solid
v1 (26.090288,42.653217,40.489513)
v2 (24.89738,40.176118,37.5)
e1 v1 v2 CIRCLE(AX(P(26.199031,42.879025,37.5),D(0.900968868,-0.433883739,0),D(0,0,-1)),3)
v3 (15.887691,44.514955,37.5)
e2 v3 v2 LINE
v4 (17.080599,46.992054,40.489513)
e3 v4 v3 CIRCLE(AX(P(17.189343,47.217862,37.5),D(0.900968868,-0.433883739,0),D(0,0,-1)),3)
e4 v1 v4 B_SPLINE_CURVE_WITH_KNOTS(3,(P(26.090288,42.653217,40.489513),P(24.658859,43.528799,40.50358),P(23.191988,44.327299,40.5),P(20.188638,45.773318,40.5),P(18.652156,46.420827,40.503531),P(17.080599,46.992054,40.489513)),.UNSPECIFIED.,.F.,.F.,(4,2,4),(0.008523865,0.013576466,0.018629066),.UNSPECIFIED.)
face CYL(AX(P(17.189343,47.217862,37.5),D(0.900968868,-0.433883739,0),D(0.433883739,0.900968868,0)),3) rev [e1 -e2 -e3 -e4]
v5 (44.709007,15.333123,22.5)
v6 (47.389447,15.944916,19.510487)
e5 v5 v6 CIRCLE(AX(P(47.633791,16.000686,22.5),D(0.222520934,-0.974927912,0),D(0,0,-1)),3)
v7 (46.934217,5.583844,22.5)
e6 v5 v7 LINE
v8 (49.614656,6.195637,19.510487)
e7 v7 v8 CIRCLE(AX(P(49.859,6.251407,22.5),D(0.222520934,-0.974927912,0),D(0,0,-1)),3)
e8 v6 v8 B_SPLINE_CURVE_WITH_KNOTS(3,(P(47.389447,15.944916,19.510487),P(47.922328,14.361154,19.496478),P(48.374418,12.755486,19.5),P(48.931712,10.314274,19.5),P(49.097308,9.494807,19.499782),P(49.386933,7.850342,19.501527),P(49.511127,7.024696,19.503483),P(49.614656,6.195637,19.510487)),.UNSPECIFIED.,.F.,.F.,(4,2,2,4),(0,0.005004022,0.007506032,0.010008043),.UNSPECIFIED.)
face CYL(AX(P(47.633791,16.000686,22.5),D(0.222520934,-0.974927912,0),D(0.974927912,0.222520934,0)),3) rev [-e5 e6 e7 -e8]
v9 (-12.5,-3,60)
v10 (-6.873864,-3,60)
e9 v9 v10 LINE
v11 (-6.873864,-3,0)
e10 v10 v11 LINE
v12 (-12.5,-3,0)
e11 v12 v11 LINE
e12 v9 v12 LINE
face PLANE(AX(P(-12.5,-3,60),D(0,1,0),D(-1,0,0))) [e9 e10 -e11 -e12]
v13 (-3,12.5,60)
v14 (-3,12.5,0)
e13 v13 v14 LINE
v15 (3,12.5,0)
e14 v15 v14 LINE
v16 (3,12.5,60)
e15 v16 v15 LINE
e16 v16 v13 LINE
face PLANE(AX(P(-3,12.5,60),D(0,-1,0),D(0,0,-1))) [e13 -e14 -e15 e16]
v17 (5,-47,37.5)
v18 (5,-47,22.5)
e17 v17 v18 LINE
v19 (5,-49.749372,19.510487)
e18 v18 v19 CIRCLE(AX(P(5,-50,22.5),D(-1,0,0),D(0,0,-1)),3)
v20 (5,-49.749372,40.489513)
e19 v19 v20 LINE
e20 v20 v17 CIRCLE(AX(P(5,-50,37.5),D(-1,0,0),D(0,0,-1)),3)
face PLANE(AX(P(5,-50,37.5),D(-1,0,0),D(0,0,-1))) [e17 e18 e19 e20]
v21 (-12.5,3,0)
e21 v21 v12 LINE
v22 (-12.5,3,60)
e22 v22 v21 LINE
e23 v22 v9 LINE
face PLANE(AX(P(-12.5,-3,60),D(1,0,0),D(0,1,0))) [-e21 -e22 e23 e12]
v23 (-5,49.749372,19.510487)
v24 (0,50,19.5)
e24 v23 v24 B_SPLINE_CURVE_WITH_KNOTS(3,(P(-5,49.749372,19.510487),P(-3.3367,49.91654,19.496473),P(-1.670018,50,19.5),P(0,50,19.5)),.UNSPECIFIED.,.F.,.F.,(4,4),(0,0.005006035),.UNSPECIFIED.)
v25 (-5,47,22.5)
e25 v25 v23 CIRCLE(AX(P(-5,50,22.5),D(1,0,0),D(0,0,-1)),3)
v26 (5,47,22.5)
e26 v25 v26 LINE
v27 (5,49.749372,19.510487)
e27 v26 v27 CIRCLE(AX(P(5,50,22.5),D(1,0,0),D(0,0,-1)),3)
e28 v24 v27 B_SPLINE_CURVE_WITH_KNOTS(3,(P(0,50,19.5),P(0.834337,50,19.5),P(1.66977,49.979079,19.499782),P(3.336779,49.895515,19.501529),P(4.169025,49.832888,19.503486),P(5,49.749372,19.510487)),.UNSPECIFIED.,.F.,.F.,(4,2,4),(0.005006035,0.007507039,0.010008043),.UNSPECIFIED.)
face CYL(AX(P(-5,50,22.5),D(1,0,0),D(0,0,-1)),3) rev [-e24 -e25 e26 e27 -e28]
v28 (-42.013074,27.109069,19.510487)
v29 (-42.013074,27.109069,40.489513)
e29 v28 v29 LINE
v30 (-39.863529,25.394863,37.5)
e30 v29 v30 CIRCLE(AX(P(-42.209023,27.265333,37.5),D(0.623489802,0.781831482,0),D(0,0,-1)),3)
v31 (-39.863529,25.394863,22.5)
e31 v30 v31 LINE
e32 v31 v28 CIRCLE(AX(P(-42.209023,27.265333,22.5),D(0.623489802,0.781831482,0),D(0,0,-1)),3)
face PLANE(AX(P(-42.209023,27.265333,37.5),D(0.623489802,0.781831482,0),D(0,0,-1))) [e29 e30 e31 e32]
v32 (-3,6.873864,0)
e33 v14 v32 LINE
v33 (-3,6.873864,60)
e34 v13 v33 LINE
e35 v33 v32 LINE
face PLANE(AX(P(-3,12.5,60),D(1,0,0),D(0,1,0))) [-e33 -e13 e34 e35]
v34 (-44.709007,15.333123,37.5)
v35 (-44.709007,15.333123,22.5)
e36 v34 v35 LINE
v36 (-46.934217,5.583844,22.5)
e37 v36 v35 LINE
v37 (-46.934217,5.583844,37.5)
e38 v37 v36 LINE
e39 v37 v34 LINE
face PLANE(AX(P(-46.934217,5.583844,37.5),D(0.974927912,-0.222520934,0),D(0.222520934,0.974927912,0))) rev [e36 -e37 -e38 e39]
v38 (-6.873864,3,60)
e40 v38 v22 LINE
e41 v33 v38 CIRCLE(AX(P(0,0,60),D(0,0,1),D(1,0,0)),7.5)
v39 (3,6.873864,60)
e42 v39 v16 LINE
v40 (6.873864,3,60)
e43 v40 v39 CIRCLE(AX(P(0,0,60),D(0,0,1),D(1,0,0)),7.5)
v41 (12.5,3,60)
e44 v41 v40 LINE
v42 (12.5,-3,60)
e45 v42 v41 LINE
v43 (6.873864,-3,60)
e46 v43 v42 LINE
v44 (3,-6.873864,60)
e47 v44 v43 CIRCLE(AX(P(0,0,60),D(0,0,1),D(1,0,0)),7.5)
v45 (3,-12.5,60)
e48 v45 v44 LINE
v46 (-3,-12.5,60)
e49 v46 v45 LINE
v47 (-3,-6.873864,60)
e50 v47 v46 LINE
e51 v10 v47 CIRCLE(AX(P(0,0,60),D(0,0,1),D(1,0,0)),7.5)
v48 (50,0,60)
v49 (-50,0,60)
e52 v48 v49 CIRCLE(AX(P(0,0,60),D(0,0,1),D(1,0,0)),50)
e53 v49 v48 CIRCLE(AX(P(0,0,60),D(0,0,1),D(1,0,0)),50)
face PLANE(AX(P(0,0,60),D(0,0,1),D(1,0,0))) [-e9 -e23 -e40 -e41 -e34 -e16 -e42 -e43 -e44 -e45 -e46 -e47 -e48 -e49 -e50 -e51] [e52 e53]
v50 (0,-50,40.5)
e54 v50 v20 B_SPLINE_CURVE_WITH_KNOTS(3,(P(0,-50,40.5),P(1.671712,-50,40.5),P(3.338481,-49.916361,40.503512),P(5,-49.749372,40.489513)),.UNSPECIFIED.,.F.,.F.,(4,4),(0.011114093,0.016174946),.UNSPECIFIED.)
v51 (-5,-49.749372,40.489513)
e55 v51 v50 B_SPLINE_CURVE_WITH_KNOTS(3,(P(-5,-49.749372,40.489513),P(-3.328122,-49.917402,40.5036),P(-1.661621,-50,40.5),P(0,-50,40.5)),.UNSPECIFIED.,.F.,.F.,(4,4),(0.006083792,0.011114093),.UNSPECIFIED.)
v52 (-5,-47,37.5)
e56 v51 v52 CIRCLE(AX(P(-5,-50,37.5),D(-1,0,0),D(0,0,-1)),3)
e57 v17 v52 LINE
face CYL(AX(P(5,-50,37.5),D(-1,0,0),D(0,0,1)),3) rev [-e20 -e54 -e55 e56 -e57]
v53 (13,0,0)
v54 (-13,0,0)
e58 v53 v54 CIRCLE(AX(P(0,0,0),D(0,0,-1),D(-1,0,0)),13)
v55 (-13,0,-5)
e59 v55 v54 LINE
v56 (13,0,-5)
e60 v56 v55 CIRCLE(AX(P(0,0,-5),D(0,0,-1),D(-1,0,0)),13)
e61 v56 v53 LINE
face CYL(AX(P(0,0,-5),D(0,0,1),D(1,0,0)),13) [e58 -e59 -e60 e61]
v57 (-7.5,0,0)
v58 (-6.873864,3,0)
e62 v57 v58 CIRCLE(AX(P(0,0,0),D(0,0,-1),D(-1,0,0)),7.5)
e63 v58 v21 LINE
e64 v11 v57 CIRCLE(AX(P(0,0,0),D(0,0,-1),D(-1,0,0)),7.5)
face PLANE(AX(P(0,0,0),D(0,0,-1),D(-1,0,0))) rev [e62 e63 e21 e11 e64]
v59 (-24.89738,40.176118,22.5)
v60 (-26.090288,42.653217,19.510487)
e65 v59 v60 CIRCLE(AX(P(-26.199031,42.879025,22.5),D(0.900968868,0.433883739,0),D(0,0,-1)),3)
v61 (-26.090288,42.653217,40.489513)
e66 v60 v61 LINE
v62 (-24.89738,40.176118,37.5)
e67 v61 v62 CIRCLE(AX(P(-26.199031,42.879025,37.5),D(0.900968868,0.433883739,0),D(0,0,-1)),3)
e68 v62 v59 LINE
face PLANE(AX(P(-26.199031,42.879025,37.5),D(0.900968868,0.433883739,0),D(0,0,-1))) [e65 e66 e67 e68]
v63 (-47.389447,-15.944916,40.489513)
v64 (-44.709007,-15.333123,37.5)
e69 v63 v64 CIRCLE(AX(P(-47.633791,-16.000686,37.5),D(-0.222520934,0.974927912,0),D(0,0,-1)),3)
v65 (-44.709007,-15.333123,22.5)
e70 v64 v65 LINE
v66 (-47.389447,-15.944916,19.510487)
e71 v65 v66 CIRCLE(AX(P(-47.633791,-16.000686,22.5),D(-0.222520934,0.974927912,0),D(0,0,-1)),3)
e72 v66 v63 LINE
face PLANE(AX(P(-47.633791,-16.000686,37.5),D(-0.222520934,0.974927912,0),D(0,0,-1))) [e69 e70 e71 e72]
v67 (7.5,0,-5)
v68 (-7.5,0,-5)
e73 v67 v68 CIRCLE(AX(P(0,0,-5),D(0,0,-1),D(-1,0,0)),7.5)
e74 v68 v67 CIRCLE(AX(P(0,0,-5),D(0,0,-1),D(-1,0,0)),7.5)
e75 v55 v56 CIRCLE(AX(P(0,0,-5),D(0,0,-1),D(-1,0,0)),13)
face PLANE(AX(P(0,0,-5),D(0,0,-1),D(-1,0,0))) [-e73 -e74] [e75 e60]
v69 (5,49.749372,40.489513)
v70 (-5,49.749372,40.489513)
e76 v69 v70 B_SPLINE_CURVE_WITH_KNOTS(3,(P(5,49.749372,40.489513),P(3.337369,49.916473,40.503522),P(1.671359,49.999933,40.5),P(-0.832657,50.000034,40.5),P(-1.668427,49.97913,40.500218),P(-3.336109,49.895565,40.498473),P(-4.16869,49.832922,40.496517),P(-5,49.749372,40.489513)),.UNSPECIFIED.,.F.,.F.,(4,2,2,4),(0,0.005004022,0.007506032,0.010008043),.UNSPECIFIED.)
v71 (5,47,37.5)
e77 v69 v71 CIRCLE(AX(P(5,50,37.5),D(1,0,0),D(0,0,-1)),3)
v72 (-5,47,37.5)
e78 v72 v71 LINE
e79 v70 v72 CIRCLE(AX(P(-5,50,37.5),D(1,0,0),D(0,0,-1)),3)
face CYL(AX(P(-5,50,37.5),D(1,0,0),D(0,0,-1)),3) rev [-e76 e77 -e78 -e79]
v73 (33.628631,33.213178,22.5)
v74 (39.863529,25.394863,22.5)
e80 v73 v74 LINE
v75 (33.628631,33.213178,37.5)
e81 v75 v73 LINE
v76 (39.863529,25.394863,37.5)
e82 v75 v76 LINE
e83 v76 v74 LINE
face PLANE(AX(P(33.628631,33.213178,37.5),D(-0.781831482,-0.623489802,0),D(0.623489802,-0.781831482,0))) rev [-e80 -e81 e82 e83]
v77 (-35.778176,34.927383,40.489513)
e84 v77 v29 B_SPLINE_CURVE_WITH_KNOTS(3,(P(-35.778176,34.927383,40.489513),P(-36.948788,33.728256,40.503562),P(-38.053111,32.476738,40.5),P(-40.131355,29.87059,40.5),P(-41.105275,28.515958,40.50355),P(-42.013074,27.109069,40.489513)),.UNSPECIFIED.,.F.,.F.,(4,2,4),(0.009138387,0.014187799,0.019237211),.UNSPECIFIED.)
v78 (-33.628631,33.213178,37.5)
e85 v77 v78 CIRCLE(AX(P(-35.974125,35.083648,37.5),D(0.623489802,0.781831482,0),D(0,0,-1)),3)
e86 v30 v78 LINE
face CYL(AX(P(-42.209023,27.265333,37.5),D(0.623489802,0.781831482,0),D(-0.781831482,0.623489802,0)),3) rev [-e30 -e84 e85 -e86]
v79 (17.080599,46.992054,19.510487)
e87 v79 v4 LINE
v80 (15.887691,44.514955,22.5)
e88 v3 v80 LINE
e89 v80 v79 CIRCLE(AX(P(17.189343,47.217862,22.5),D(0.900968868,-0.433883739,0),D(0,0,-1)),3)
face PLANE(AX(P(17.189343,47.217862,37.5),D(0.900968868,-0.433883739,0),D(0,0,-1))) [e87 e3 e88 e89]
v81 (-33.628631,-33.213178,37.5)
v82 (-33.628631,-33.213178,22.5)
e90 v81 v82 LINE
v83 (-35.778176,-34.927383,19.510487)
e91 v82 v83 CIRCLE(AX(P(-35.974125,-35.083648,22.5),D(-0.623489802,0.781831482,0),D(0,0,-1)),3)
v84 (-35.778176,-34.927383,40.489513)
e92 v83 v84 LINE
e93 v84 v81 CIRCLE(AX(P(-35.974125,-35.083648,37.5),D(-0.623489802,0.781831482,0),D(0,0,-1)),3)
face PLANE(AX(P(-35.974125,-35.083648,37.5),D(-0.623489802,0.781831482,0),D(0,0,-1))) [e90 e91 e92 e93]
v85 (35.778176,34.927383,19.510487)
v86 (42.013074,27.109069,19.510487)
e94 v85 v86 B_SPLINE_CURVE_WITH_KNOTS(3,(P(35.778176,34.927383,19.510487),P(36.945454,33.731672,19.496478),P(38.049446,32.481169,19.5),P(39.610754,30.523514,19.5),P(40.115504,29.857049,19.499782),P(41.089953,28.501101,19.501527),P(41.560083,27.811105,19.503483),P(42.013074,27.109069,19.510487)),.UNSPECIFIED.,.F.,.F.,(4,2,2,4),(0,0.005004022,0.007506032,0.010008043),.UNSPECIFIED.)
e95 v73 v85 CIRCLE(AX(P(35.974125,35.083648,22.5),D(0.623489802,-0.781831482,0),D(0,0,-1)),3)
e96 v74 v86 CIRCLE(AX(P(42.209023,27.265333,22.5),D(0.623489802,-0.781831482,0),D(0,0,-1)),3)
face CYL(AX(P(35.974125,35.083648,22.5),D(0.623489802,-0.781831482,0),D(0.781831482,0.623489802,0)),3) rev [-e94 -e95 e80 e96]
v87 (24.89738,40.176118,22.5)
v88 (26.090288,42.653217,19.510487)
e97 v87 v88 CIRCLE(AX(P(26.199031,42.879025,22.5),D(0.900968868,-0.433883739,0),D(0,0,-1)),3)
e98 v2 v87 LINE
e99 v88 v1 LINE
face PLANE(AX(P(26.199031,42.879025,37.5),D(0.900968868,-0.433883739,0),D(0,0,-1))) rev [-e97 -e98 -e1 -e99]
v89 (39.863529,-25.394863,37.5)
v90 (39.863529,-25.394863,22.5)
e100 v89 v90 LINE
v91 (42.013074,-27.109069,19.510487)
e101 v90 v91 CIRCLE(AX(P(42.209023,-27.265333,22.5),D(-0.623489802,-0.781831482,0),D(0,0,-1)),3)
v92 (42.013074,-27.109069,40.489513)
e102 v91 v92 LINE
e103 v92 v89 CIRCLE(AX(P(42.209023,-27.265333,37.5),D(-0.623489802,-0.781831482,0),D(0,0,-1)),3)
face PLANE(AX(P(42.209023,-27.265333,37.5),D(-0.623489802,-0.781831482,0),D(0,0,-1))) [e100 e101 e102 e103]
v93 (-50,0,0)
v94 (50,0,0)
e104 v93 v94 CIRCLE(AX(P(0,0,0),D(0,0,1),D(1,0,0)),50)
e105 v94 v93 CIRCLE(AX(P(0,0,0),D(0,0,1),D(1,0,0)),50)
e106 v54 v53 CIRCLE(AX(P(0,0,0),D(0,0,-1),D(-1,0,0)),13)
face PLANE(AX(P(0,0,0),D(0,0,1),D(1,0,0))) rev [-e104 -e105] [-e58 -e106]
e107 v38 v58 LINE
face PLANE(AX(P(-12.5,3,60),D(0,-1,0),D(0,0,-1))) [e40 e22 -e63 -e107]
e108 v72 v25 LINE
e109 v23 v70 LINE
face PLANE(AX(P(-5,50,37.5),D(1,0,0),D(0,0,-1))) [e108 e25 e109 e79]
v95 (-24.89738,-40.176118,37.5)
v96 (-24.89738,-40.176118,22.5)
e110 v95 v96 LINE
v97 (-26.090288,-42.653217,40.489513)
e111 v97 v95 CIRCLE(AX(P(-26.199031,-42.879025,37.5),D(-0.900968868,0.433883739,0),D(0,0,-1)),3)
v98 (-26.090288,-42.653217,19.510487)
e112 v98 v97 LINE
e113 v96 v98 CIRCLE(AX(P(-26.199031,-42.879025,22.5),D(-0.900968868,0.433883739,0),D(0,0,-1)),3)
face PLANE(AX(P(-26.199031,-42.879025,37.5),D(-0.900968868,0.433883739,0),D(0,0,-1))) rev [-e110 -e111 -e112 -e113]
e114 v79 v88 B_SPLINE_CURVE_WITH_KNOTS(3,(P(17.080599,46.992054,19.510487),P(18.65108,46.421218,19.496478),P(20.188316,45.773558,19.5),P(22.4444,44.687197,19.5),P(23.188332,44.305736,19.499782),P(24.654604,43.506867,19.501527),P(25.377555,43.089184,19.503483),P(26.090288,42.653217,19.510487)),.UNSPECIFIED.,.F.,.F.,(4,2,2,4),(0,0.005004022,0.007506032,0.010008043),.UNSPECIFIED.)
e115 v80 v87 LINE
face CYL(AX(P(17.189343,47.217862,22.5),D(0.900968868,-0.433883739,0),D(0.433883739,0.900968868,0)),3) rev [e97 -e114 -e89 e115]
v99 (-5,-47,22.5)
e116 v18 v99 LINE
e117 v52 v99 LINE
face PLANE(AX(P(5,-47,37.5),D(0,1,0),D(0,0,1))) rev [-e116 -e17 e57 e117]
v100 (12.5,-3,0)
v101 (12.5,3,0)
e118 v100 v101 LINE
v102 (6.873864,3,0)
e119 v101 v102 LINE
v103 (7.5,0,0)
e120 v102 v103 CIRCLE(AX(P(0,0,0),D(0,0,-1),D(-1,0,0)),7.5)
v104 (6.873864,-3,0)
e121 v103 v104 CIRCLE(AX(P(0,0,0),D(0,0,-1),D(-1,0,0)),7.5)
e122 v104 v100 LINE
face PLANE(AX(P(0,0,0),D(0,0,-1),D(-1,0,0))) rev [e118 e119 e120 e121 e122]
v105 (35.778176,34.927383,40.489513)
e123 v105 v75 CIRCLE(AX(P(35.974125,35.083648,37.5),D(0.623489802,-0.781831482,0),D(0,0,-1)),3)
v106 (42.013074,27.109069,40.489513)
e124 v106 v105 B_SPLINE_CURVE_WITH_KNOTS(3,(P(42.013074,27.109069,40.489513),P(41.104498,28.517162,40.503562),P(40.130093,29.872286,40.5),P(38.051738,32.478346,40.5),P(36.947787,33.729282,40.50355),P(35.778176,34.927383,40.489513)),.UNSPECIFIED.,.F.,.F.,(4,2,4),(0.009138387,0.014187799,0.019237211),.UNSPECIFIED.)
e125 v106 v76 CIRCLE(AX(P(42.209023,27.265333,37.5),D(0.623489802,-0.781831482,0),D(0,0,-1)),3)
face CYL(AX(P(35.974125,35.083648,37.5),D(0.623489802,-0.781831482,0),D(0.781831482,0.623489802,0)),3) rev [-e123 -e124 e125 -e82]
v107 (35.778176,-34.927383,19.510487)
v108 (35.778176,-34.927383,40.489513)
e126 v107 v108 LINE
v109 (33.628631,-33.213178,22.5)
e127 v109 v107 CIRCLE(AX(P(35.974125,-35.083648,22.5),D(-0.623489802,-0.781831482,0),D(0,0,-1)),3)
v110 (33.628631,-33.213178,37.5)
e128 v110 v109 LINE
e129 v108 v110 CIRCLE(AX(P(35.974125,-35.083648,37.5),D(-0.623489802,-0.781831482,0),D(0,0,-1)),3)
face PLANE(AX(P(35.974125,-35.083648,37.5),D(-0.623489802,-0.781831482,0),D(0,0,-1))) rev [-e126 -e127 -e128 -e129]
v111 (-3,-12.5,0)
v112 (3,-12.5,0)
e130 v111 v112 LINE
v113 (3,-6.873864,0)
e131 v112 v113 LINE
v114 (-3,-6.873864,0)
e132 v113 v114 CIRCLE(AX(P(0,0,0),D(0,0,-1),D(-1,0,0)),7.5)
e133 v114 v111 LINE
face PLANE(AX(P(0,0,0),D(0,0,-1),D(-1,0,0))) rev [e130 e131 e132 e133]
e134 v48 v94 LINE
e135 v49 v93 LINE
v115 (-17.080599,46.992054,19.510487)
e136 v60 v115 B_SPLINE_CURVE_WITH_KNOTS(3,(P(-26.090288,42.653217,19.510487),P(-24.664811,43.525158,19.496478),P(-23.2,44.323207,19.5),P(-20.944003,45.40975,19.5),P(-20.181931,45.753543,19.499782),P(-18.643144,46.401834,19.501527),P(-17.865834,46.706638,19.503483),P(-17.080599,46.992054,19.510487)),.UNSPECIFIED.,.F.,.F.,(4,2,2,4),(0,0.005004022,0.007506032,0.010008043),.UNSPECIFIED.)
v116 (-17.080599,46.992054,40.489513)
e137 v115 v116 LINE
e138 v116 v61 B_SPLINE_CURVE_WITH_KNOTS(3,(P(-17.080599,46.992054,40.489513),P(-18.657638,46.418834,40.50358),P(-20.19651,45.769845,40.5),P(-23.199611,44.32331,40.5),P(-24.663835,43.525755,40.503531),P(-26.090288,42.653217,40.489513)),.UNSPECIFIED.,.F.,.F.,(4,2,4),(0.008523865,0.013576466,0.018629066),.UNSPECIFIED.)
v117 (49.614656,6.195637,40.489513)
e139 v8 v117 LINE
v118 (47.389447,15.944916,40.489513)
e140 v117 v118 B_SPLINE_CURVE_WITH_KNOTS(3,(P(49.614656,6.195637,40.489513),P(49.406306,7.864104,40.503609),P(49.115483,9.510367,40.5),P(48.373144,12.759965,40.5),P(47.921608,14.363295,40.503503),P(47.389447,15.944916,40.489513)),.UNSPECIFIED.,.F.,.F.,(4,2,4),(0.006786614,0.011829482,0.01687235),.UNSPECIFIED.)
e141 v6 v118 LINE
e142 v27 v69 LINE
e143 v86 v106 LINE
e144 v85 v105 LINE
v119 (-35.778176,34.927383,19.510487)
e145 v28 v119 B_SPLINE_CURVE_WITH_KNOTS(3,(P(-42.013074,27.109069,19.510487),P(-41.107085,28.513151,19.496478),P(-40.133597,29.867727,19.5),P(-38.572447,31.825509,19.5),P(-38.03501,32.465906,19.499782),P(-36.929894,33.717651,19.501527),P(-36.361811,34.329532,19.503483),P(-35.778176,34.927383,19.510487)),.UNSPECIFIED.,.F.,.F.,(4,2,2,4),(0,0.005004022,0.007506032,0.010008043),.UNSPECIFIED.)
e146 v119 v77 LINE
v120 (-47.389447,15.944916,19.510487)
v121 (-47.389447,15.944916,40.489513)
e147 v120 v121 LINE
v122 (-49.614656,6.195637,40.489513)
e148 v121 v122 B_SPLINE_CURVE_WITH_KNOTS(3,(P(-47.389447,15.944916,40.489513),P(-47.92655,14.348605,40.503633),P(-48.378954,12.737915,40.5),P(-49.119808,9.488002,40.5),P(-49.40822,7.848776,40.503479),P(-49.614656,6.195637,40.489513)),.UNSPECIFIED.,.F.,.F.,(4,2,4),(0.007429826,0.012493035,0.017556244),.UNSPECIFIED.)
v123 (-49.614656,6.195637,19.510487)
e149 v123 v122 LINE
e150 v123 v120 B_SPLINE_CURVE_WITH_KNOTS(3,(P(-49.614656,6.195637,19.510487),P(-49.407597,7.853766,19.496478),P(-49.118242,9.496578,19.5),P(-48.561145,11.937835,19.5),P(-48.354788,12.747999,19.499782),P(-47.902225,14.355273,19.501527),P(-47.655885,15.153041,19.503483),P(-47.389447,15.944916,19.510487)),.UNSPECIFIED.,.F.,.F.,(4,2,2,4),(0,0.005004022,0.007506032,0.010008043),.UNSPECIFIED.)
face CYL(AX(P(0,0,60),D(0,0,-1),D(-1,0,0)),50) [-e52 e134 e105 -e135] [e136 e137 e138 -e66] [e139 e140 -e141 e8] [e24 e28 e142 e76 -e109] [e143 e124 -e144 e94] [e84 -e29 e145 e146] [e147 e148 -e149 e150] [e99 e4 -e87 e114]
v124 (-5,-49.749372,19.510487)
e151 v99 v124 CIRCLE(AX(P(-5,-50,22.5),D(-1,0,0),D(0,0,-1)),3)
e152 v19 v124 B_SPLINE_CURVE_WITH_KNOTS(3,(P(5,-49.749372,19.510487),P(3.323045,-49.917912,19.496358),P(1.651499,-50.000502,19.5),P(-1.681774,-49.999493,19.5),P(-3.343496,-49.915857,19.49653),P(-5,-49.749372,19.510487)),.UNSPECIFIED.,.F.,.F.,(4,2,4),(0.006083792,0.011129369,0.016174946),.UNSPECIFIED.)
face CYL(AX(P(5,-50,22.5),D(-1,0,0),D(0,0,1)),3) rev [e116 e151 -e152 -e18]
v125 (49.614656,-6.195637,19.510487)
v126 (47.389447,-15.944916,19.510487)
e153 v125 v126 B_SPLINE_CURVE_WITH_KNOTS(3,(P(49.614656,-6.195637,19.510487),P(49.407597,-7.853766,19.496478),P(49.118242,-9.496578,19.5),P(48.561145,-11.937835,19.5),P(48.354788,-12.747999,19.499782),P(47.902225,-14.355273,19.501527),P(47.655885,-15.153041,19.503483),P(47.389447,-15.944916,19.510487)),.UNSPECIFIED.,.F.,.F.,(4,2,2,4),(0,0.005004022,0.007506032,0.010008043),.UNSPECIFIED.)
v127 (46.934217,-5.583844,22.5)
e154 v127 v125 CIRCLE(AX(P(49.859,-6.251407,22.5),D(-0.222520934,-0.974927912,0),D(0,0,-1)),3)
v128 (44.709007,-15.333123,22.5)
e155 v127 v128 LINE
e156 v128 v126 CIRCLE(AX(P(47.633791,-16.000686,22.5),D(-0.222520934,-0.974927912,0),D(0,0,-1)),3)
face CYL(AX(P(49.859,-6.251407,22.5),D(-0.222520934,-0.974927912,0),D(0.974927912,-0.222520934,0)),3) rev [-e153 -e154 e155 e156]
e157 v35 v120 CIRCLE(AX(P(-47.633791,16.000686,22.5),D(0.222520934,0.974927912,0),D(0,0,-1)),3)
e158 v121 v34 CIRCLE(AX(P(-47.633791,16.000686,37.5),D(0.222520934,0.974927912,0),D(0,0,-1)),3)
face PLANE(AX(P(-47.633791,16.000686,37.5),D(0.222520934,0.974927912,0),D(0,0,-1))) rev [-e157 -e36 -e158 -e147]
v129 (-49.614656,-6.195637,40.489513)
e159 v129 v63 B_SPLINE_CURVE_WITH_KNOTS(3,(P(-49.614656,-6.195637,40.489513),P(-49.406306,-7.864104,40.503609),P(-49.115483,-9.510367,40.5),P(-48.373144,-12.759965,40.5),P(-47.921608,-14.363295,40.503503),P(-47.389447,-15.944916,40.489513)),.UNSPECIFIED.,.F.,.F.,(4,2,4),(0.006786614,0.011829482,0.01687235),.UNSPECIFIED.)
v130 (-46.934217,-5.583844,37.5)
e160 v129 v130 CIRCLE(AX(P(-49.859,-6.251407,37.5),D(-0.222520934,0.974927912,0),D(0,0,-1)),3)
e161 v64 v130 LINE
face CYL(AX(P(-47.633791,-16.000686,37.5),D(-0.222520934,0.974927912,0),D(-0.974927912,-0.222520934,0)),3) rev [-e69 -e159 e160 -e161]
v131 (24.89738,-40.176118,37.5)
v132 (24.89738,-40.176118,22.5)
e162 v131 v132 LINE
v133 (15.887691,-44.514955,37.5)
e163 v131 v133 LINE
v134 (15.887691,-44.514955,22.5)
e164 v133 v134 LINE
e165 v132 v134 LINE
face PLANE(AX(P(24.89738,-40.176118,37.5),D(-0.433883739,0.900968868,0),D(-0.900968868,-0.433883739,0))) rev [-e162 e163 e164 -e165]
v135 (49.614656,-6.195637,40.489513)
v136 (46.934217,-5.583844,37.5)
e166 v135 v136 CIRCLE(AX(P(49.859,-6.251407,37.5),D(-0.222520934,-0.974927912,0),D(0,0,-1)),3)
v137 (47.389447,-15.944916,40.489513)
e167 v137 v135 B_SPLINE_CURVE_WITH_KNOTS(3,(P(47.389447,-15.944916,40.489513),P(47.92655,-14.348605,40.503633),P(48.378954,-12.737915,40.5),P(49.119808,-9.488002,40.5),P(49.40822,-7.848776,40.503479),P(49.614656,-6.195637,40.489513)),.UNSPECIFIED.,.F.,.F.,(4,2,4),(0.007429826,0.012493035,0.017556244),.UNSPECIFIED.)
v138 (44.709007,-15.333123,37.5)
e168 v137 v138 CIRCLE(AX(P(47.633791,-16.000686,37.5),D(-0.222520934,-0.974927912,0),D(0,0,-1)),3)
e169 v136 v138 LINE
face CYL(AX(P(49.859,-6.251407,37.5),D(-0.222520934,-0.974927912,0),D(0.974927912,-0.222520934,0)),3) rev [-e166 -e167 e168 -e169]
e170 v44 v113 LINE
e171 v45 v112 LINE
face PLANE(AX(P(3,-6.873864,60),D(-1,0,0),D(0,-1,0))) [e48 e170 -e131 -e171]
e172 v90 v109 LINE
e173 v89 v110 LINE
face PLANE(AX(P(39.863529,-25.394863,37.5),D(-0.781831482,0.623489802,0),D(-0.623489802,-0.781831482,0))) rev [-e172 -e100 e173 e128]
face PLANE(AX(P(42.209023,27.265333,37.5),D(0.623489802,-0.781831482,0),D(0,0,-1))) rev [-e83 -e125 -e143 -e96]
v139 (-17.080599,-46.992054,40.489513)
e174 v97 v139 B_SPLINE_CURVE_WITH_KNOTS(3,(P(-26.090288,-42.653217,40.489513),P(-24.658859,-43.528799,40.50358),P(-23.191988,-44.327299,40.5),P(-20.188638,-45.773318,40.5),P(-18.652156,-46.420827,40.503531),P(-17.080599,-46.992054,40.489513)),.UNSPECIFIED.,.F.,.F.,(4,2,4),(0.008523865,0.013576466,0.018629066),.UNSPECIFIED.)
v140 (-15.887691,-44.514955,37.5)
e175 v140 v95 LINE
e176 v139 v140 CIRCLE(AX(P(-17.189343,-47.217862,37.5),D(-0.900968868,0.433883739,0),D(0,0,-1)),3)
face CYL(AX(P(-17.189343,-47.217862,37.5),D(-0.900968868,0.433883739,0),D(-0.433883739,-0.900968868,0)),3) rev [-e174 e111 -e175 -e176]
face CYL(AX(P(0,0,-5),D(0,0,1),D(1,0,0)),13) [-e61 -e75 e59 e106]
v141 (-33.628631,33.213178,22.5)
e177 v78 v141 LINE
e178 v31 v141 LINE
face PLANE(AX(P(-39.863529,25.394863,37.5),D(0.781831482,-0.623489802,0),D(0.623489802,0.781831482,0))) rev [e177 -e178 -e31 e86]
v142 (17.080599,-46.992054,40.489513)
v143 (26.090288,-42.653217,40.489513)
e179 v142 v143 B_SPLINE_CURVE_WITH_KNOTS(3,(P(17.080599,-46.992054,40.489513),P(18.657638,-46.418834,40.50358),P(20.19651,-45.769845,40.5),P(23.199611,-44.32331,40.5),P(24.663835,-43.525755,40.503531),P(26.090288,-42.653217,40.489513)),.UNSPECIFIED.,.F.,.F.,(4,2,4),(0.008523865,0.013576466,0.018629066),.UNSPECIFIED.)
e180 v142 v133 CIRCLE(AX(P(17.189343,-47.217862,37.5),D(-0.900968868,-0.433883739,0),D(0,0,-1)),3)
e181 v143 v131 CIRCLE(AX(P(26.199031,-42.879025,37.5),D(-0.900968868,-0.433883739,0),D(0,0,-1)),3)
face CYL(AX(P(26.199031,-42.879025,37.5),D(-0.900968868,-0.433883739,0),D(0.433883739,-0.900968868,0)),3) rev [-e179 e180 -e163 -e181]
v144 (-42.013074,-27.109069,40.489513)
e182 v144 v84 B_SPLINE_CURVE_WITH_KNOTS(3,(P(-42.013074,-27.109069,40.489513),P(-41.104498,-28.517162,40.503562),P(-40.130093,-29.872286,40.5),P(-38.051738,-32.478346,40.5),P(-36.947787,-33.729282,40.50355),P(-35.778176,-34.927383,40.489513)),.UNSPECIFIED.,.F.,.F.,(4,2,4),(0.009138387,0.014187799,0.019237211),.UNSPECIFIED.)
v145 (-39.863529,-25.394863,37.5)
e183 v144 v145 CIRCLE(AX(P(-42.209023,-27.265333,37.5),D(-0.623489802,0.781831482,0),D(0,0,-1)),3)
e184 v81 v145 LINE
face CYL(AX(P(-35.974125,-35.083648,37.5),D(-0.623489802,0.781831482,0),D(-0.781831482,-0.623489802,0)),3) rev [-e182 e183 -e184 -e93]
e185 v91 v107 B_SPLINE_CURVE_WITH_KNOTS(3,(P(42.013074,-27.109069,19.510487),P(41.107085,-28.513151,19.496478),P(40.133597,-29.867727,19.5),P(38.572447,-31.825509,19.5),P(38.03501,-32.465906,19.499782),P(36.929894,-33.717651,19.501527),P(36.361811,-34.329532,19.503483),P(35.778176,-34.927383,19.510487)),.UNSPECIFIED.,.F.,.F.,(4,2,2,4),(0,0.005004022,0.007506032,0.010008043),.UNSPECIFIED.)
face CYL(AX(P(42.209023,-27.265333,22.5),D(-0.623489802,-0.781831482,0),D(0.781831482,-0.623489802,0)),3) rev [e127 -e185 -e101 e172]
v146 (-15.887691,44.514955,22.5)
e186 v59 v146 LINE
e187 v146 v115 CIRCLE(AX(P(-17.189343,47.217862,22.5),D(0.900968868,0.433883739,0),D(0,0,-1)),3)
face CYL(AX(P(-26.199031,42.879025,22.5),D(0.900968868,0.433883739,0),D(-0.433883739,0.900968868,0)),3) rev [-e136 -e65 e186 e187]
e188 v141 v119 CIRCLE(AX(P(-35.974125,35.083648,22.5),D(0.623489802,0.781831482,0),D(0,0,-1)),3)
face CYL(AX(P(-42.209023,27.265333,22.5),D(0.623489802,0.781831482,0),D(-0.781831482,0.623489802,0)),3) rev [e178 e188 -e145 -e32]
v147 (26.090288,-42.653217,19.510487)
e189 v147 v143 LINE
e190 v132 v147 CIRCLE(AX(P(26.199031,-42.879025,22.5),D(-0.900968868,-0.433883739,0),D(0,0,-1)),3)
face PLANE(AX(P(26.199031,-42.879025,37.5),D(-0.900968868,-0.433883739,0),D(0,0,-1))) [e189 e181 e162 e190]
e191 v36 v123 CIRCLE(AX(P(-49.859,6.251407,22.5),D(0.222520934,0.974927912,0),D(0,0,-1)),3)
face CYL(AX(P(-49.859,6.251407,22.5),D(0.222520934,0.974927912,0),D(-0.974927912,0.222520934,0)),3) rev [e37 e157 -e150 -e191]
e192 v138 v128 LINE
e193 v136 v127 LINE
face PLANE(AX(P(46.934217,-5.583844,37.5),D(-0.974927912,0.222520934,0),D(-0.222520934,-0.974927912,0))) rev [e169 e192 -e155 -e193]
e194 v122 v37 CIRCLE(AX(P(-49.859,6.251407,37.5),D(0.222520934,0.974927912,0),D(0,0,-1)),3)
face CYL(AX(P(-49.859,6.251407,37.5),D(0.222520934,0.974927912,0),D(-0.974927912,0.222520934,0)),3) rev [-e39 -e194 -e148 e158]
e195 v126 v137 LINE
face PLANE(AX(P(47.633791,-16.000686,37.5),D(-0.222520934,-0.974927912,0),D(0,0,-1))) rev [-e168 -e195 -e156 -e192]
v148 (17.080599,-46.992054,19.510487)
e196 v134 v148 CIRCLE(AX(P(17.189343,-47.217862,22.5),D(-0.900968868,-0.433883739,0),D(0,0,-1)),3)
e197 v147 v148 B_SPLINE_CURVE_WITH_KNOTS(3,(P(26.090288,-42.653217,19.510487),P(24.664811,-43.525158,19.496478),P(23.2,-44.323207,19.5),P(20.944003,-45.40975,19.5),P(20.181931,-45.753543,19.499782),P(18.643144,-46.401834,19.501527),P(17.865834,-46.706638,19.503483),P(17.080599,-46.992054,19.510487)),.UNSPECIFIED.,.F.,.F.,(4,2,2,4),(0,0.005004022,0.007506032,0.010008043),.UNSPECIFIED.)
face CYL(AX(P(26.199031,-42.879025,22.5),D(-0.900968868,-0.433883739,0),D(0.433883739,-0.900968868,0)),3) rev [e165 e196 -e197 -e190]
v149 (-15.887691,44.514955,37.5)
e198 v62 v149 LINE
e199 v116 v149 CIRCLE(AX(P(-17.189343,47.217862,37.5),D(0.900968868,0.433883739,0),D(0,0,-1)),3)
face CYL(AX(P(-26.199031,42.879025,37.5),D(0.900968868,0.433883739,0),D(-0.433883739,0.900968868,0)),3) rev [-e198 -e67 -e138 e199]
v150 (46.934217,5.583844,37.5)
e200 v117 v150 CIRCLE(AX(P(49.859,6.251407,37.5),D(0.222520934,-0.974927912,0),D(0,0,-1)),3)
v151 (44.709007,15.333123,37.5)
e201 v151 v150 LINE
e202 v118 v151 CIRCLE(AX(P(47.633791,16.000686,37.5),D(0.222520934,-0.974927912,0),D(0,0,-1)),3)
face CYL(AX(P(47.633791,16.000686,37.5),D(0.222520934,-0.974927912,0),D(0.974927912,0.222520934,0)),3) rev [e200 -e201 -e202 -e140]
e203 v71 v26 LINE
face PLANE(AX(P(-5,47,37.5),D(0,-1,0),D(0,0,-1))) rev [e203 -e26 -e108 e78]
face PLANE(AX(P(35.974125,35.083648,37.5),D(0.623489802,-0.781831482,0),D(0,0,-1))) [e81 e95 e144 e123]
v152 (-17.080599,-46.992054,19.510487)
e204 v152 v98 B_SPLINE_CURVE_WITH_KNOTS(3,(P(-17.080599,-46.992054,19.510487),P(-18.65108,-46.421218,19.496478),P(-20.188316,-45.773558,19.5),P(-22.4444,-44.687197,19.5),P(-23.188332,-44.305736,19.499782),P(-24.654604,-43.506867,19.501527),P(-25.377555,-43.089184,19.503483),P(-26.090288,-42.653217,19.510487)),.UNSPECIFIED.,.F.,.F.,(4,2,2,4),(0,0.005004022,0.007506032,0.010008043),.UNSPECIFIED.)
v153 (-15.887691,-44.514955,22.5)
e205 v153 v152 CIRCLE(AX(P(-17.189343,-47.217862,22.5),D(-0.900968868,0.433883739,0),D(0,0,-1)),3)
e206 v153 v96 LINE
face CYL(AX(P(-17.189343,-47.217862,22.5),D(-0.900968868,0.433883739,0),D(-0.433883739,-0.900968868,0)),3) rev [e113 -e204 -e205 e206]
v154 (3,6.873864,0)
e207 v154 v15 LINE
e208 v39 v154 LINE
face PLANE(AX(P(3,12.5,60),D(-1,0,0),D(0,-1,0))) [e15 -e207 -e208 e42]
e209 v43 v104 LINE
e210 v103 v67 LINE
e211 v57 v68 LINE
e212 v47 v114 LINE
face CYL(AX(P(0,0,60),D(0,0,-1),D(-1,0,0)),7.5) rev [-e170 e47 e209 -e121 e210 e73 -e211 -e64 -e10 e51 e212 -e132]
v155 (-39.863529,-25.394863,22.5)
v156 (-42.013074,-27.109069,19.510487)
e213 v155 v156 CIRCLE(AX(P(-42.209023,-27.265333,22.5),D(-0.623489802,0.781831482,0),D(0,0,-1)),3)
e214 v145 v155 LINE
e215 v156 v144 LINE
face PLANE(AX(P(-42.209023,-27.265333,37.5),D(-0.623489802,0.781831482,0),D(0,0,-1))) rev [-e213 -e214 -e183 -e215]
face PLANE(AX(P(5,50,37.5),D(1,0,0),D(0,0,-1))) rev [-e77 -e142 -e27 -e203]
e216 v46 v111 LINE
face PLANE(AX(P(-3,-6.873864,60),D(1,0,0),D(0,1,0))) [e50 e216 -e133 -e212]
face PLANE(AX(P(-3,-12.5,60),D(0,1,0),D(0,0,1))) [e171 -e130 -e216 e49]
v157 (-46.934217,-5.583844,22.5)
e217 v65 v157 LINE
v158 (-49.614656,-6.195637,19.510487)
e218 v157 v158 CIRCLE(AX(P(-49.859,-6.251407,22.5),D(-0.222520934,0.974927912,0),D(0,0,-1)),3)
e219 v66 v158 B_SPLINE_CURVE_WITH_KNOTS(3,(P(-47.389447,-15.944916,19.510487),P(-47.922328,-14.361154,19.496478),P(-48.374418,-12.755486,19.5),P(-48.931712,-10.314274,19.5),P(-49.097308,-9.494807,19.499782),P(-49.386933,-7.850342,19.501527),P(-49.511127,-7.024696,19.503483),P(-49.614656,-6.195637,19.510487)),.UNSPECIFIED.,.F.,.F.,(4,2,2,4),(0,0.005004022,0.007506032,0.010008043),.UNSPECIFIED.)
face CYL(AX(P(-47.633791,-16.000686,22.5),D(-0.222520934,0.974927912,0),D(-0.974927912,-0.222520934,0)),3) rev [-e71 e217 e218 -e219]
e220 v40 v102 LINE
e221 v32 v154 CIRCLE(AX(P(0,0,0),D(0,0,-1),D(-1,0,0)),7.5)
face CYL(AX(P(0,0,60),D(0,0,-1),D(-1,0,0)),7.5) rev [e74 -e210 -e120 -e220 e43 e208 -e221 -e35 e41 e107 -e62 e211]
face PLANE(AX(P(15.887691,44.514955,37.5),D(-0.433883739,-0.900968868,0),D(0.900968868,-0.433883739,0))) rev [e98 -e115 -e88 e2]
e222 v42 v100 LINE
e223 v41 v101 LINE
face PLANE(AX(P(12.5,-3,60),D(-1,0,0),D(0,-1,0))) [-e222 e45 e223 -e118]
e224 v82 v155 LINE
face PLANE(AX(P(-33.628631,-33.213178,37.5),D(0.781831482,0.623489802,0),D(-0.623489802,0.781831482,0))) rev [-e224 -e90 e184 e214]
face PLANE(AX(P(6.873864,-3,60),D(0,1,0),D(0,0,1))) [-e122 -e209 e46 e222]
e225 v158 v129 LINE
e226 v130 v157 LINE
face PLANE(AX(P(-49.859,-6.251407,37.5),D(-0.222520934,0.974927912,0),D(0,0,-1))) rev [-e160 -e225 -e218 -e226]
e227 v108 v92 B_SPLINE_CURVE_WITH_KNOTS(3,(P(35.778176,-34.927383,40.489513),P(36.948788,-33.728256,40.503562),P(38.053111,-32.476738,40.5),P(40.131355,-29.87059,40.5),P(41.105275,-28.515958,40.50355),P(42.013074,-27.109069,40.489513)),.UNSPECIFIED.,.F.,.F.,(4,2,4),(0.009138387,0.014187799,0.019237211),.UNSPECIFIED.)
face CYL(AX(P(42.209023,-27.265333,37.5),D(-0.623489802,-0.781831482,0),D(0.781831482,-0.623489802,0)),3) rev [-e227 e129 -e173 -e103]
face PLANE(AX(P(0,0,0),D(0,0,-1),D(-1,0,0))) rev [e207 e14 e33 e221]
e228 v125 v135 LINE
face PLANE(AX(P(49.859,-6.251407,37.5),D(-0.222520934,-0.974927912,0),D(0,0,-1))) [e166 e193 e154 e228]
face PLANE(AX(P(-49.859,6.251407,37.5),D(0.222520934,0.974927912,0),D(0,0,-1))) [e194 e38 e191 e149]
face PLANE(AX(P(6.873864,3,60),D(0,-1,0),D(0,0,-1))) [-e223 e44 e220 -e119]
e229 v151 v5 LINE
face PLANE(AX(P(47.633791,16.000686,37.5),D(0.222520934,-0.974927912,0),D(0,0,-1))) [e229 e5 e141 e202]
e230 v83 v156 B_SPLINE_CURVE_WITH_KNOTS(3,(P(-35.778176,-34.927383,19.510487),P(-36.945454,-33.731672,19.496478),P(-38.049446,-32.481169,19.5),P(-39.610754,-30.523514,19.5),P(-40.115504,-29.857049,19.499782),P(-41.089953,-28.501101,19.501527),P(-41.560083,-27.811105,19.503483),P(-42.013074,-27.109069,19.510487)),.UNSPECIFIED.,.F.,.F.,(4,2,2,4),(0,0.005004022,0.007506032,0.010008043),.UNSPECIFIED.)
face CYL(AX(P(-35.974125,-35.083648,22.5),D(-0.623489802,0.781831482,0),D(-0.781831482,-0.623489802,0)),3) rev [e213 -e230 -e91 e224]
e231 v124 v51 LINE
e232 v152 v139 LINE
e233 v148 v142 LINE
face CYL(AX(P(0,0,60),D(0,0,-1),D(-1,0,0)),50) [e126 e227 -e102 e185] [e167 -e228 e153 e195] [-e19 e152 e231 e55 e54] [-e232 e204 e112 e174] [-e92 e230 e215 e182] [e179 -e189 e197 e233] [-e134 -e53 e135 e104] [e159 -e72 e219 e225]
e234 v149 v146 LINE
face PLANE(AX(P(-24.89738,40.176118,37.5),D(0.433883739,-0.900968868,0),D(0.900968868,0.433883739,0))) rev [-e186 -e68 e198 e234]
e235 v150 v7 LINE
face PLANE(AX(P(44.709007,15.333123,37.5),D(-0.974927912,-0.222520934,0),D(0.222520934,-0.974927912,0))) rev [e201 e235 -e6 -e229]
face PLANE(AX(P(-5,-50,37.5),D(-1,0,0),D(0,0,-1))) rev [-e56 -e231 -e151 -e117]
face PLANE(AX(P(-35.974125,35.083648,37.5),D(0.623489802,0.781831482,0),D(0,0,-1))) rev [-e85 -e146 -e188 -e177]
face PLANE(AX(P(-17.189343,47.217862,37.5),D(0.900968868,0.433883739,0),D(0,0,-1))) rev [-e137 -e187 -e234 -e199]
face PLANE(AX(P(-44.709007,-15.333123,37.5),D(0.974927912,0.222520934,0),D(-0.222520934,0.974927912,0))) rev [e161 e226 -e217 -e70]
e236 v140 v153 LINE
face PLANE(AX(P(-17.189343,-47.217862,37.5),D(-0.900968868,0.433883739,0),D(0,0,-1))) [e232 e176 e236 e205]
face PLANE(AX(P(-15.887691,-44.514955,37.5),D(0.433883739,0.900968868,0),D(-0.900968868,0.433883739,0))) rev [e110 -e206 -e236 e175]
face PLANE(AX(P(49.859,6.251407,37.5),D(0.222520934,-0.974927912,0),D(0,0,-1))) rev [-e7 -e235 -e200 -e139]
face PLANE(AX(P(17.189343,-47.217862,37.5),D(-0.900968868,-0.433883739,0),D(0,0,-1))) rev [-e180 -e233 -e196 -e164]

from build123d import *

# Parameters (mm, degrees)
SKETCH_1_R               = 50
EXTRUDE_1_DEPTH          = 60
EXTRUDE_START            = 5
SKETCH_2_R               = 13
SKETCH_2_R_2             = 7.5
EXTRUDE_1_2_DEPTH        = 5
CUT_EXTRUDE_1_DEPTH      = 5
PATTERN_CIRCULAR_1_COUNT = 14


with BuildPart() as part:
    # 草图1 → Extrude 1 (new body)
    with BuildSketch(Plane.XY):
        with Locations(Location((0, 0, 0), (0, 0, 180))):
            Circle(SKETCH_1_R)
        with BuildLine():
            Line((3, -6.873863542), (3, -12.5))
            Line((3, -12.5), (-3, -12.5))
            Line((-3, -12.5), (-3, -6.873863542))
            ThreePointArc((-3, -6.873863542), (-5.303300859, -5.303300859), (-6.873863542, -3))
            Line((-6.873863542, -3), (-12.5, -3))
            Line((-12.5, -3), (-12.5, 3))
            Line((-12.5, 3), (-6.873863542, 3))
            ThreePointArc((-6.873863542, 3), (-5.303300859, 5.303300859), (-3, 6.873863542))
            Line((-3, 6.873863542), (-3, 12.5))
            Line((-3, 12.5), (3, 12.5))
            Line((3, 12.5), (3, 6.873863542))
            ThreePointArc((3, 6.873863542), (5.303300859, 5.303300859), (6.873863542, 3))
            Line((6.873863542, 3), (12.5, 3))
            Line((12.5, 3), (12.5, -3))
            Line((12.5, -3), (6.873863542, -3))
            ThreePointArc((6.873863542, -3), (5.303300859, -5.303300859), (3, -6.873863542))
        make_face(mode=Mode.SUBTRACT)
    extrude(amount=EXTRUDE_1_DEPTH)

    # 草图2 → Extrude 1 2 (add)
    with BuildSketch(Plane(origin=(0, 0, 0), x_dir=(-1, 0, 0), z_dir=(0, 0, -1)).offset(EXTRUDE_START)):
        Circle(SKETCH_2_R)
        Circle(SKETCH_2_R_2, mode=Mode.SUBTRACT)
    extrude(amount=-EXTRUDE_1_2_DEPTH)

    # 草图3 → 切除-拉伸1 (cut, symmetric)
    with BuildSketch(Plane(origin=(0, 0, 0), x_dir=(0, 0, -1), z_dir=(1, 0, 0))):
        with BuildLine():
            Line((-37.5, 53), (-22.5, 53))
            ThreePointArc((-22.5, 53), (-19.5, 50), (-22.5, 47))
            Line((-22.5, 47), (-37.5, 47))
            ThreePointArc((-37.5, 47), (-40.5, 50), (-37.5, 53))
        make_face()
    cut_extrude_1 = extrude(amount=CUT_EXTRUDE_1_DEPTH, both=True, mode=Mode.SUBTRACT)

    # 阵列(圆周)1: 切除-拉伸1 ×14 about axis
    pattern_circular_1_axis = Axis((0, 0, 0), (0, 0, 1))
    for i in range(1, PATTERN_CIRCULAR_1_COUNT):
        add(cut_extrude_1.rotate(pattern_circular_1_axis, i * 360 / PATTERN_CIRCULAR_1_COUNT), mode=Mode.SUBTRACT)


solid = part.part
